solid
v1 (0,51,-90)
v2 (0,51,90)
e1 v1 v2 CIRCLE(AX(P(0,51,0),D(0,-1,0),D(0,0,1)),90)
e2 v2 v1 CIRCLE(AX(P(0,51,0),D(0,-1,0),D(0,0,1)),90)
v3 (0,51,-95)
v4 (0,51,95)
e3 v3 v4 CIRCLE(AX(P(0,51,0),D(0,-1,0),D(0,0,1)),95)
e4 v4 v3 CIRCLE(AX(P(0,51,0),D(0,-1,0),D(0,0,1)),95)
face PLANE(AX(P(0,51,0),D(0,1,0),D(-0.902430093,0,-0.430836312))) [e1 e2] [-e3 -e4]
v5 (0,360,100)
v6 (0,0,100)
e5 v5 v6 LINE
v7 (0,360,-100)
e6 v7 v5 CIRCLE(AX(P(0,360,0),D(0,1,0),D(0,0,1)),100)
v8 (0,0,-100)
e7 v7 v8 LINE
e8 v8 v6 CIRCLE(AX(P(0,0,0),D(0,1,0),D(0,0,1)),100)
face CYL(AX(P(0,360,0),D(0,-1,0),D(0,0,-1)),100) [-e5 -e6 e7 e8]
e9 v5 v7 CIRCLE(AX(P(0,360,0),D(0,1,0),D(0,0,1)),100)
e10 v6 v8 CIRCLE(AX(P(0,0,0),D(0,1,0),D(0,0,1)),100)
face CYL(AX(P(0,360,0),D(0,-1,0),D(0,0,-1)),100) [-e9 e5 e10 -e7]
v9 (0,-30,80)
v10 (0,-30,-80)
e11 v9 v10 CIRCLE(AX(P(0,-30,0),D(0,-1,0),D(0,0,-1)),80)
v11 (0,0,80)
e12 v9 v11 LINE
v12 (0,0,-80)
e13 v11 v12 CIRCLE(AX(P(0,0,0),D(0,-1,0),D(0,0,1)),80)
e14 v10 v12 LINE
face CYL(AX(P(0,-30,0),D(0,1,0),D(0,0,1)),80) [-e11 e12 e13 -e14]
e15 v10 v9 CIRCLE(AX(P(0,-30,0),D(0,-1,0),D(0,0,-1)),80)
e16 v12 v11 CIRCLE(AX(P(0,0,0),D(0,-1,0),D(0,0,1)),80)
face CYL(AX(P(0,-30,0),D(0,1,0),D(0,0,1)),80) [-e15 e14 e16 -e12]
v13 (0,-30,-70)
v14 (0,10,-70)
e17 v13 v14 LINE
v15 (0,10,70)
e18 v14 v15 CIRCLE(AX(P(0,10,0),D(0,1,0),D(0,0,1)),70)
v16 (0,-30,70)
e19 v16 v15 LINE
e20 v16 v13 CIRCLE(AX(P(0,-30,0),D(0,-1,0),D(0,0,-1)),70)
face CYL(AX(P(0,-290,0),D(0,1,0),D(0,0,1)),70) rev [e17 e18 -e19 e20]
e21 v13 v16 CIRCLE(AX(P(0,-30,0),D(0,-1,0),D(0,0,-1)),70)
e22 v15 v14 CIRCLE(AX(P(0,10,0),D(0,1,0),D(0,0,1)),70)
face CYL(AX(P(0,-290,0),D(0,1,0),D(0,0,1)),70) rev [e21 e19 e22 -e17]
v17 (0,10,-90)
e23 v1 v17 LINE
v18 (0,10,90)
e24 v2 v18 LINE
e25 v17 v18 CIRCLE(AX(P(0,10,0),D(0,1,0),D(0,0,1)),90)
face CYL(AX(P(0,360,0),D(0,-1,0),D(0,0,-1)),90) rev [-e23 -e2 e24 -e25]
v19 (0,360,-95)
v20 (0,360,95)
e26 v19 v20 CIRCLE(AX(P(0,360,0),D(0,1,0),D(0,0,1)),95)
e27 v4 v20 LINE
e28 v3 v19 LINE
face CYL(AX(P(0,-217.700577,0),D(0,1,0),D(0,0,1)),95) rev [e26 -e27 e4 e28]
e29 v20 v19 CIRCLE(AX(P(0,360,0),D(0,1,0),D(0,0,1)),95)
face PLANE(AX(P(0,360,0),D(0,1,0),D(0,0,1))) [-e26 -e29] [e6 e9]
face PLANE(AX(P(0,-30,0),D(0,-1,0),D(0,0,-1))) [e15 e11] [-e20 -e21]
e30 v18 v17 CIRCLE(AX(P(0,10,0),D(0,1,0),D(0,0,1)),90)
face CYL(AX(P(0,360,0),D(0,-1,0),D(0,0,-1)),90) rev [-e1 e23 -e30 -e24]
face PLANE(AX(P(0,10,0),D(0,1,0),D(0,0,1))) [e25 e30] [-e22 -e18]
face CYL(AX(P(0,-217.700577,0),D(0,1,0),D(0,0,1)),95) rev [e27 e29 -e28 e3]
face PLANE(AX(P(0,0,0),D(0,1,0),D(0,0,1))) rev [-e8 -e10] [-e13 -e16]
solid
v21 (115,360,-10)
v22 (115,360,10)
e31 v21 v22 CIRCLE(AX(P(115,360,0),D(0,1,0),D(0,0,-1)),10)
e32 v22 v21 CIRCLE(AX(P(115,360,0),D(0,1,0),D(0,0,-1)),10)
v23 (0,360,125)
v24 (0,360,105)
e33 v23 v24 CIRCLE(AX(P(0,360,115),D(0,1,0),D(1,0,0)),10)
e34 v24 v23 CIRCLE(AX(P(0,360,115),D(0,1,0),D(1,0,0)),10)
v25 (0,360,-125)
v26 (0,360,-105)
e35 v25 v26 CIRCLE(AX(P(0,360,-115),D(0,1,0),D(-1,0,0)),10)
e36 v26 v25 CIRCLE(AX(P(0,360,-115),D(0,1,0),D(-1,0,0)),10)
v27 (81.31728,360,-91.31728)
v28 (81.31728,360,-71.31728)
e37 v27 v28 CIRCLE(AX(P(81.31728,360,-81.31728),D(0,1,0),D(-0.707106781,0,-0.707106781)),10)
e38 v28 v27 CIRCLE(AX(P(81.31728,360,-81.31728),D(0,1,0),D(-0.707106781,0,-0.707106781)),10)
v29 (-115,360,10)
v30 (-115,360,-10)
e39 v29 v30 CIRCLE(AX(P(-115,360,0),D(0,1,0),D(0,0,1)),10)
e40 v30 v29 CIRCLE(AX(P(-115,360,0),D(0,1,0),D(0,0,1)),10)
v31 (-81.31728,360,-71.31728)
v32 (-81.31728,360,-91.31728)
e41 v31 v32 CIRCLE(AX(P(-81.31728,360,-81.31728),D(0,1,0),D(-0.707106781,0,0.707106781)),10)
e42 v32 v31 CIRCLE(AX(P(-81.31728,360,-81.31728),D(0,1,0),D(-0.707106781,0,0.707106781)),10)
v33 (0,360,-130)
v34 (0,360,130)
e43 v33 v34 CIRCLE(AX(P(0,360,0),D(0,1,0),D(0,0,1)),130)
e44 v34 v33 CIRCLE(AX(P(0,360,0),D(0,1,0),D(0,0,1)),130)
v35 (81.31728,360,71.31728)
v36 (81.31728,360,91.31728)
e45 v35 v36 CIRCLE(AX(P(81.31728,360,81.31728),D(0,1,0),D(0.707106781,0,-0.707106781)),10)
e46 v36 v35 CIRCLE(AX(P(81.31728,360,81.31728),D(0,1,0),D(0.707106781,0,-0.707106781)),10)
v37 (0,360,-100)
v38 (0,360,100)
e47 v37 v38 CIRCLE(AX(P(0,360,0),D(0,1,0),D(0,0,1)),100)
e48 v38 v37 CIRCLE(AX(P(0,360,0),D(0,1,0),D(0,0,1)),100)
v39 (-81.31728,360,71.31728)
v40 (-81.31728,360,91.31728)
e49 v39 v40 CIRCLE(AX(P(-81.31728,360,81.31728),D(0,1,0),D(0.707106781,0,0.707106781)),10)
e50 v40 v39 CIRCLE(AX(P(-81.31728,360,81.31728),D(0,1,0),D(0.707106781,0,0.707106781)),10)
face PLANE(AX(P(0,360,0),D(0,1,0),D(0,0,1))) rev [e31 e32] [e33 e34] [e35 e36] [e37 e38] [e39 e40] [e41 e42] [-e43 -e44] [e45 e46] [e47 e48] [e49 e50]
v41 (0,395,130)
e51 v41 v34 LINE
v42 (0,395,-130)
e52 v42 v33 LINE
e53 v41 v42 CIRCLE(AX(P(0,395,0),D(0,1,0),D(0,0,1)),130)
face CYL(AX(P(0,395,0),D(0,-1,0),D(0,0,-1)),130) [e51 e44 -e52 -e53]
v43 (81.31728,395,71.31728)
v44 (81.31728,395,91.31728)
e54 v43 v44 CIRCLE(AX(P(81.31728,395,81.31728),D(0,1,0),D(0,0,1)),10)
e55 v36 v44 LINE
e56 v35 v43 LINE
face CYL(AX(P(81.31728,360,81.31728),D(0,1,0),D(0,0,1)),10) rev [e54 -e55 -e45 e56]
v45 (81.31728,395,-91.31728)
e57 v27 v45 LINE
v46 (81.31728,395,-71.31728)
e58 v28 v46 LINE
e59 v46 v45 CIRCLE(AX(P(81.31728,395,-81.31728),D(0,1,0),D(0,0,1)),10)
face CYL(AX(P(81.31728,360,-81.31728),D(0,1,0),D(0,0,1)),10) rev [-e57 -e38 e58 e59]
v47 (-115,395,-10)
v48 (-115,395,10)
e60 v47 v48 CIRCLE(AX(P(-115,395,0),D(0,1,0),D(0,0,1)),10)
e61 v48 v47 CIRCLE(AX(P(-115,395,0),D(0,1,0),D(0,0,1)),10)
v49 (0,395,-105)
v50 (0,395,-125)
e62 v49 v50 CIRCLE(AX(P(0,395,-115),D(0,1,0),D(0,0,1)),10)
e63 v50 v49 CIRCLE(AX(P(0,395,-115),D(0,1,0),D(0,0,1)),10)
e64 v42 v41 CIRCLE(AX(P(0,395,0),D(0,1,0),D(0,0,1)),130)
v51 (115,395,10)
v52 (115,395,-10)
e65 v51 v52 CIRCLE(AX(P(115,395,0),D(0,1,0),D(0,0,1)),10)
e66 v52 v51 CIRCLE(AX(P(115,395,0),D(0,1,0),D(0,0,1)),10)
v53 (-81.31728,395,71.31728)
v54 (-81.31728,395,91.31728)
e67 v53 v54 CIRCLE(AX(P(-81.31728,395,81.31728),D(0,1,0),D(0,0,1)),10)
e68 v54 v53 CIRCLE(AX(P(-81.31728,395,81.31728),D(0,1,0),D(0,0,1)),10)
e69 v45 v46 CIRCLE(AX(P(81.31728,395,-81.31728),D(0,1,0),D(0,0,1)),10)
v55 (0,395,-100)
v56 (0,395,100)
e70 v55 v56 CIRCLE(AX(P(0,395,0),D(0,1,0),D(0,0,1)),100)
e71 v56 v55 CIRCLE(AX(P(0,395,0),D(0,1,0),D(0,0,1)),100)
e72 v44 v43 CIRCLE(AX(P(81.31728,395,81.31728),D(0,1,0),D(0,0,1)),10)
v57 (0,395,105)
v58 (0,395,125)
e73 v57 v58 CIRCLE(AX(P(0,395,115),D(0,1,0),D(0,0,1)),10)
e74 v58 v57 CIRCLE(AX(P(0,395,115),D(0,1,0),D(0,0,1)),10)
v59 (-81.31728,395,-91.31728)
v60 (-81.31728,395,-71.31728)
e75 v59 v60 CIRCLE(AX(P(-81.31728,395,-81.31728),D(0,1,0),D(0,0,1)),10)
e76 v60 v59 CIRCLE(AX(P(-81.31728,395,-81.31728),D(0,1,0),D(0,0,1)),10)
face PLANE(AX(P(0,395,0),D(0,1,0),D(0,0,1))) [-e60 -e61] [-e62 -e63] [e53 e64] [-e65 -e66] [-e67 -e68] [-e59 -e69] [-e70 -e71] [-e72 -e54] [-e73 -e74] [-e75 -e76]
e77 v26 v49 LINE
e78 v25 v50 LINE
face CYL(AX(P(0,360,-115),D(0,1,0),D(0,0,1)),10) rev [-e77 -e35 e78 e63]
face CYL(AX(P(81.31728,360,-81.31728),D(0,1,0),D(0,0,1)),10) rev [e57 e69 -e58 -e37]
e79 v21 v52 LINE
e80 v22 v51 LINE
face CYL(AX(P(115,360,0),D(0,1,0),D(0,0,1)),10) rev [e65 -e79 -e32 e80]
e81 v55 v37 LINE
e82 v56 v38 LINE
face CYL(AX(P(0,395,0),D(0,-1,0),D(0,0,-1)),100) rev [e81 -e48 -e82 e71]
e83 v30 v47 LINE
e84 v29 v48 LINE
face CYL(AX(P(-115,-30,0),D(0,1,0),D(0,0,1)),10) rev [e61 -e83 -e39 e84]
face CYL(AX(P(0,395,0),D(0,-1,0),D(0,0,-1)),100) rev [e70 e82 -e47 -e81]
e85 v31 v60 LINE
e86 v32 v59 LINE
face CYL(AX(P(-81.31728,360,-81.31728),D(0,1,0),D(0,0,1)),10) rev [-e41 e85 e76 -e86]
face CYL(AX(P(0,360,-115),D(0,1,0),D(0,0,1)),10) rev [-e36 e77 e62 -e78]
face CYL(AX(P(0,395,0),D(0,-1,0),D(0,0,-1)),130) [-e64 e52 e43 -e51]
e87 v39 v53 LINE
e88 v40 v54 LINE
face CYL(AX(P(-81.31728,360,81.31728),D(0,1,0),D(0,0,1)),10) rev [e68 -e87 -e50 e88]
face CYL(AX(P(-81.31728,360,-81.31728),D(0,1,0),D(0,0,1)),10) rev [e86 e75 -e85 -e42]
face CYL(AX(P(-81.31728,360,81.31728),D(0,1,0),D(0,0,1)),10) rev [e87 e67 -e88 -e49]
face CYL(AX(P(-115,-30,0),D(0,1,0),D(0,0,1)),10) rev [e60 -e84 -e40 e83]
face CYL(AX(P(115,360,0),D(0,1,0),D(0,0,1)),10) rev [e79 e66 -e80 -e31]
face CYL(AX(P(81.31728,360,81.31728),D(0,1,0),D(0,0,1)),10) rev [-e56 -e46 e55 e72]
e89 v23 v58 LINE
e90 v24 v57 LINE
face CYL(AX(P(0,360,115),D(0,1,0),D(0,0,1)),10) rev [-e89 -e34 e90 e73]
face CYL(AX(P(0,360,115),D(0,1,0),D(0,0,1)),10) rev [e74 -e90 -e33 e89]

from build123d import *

# Parameters (mm, degrees)
SKETCH1_R               = 100
BOSS_EXTRUDE1_DEPTH     = 360
SHELL1_T                = -10
SKETCH2_R               = 70
CUT_EXTRUDE1_DEPTH      = 300
SKETCH3_R               = 80
SKETCH3_R_2             = 70
BOSS_EXTRUDE2_DEPTH     = 30
SKETCH4_R               = 130
SKETCH4_R_2             = 100
BOSS_EXTRUDE3_DEPTH     = 35
CUT_EXTRUDE3_DEPTH      = 432.161222746
CUT_EXTRUDE3_DEPTH_BACK = 309
SKETCH6_R               = 95
SKETCH6_R_2             = 90
SKETCH7_R               = 10
CUT_EXTRUDE6_DEPTH      = 464.060471213
CIRPATTERN1_COUNT       = 8


with BuildPart() as part:
    # Sketch1 → Boss-Extrude1 (new body)
    with BuildSketch(Plane(origin=(0, 0, 0), x_dir=(1, 0, 0), z_dir=(0, 1, 0))):
        with Locations(Location((0, 0, 0), (0, 0, 90))):
            Circle(SKETCH1_R)
    extrude(amount=BOSS_EXTRUDE1_DEPTH)

    # Shell1
    shell1_openings = [part.faces().sort_by_distance(p)[0] for p in [
        (0, 360, 0),
    ]]
    offset(amount=SHELL1_T, openings=shell1_openings, kind=Kind.INTERSECTION)

    # Sketch2 → Cut-Extrude1 (cut)
    with BuildSketch(Plane(origin=(0, 10, 0), x_dir=(1, 0, 0), z_dir=(0, 1, 0))):
        with Locations(Location((0, 0, 0), (0, 0, 270))):
            Circle(SKETCH2_R)
    extrude(amount=-CUT_EXTRUDE1_DEPTH, mode=Mode.SUBTRACT)

    # Sketch3 → Boss-Extrude2 (add)
    with BuildSketch(Plane.XZ):
        with Locations(Location((0, 0, 0), (0, 0, 90))):
            Circle(SKETCH3_R)
        with Locations(Location((0, 0, 0), (0, 0, 90))):
            Circle(SKETCH3_R_2, mode=Mode.SUBTRACT)
    extrude(amount=BOSS_EXTRUDE2_DEPTH)

    # Sketch6 → Cut-Extrude3 (cut, two sides: drawn at the far end of the back side and taken through both)
    with BuildSketch(Plane(origin=(0, 360, 0), x_dir=(1, 0, 0), z_dir=(0, 1, 0)).offset(-CUT_EXTRUDE3_DEPTH_BACK)):
        with Locations(Location((0, 0, 0), (0, 0, 270))):
            Circle(SKETCH6_R)
        with Locations(Location((0, 0, 0), (0, 0, 90))):
            Circle(SKETCH6_R_2, mode=Mode.SUBTRACT)
    extrude(amount=CUT_EXTRUDE3_DEPTH + CUT_EXTRUDE3_DEPTH_BACK, mode=Mode.SUBTRACT)


with BuildPart() as body_2:
    # Sketch4 → Boss-Extrude3 (new body)
    with BuildSketch(Plane(origin=(0, 360, 0), x_dir=(1, 0, 0), z_dir=(0, 1, 0))):
        with Locations(Location((0, 0, 0), (0, 0, 270))):
            Circle(SKETCH4_R)
        with Locations(Location((0, 0, 0), (0, 0, 270))):
            Circle(SKETCH4_R_2, mode=Mode.SUBTRACT)
    extrude(amount=BOSS_EXTRUDE3_DEPTH)

    # Sketch7 → Cut-Extrude6 (cut, symmetric)
    with BuildSketch(Plane(origin=(0, 395, 0), x_dir=(1, 0, 0), z_dir=(0, 1, 0))):
        with Locations(Location((-115, 0, 0), (0, 0, 270))):
            Circle(SKETCH7_R)
    cut_extrude6 = extrude(amount=CUT_EXTRUDE6_DEPTH, both=True, mode=Mode.SUBTRACT)

    # CirPattern1: Cut-Extrude6 ×8 about axis
    cirpattern1_axis = Axis((0, 0, 0), (0, 1, 0))
    for i in range(1, CIRPATTERN1_COUNT):
        add(cut_extrude6.rotate(cirpattern1_axis, i * 360 / CIRPATTERN1_COUNT), mode=Mode.SUBTRACT)


solid = Compound([part.part, body_2.part])
